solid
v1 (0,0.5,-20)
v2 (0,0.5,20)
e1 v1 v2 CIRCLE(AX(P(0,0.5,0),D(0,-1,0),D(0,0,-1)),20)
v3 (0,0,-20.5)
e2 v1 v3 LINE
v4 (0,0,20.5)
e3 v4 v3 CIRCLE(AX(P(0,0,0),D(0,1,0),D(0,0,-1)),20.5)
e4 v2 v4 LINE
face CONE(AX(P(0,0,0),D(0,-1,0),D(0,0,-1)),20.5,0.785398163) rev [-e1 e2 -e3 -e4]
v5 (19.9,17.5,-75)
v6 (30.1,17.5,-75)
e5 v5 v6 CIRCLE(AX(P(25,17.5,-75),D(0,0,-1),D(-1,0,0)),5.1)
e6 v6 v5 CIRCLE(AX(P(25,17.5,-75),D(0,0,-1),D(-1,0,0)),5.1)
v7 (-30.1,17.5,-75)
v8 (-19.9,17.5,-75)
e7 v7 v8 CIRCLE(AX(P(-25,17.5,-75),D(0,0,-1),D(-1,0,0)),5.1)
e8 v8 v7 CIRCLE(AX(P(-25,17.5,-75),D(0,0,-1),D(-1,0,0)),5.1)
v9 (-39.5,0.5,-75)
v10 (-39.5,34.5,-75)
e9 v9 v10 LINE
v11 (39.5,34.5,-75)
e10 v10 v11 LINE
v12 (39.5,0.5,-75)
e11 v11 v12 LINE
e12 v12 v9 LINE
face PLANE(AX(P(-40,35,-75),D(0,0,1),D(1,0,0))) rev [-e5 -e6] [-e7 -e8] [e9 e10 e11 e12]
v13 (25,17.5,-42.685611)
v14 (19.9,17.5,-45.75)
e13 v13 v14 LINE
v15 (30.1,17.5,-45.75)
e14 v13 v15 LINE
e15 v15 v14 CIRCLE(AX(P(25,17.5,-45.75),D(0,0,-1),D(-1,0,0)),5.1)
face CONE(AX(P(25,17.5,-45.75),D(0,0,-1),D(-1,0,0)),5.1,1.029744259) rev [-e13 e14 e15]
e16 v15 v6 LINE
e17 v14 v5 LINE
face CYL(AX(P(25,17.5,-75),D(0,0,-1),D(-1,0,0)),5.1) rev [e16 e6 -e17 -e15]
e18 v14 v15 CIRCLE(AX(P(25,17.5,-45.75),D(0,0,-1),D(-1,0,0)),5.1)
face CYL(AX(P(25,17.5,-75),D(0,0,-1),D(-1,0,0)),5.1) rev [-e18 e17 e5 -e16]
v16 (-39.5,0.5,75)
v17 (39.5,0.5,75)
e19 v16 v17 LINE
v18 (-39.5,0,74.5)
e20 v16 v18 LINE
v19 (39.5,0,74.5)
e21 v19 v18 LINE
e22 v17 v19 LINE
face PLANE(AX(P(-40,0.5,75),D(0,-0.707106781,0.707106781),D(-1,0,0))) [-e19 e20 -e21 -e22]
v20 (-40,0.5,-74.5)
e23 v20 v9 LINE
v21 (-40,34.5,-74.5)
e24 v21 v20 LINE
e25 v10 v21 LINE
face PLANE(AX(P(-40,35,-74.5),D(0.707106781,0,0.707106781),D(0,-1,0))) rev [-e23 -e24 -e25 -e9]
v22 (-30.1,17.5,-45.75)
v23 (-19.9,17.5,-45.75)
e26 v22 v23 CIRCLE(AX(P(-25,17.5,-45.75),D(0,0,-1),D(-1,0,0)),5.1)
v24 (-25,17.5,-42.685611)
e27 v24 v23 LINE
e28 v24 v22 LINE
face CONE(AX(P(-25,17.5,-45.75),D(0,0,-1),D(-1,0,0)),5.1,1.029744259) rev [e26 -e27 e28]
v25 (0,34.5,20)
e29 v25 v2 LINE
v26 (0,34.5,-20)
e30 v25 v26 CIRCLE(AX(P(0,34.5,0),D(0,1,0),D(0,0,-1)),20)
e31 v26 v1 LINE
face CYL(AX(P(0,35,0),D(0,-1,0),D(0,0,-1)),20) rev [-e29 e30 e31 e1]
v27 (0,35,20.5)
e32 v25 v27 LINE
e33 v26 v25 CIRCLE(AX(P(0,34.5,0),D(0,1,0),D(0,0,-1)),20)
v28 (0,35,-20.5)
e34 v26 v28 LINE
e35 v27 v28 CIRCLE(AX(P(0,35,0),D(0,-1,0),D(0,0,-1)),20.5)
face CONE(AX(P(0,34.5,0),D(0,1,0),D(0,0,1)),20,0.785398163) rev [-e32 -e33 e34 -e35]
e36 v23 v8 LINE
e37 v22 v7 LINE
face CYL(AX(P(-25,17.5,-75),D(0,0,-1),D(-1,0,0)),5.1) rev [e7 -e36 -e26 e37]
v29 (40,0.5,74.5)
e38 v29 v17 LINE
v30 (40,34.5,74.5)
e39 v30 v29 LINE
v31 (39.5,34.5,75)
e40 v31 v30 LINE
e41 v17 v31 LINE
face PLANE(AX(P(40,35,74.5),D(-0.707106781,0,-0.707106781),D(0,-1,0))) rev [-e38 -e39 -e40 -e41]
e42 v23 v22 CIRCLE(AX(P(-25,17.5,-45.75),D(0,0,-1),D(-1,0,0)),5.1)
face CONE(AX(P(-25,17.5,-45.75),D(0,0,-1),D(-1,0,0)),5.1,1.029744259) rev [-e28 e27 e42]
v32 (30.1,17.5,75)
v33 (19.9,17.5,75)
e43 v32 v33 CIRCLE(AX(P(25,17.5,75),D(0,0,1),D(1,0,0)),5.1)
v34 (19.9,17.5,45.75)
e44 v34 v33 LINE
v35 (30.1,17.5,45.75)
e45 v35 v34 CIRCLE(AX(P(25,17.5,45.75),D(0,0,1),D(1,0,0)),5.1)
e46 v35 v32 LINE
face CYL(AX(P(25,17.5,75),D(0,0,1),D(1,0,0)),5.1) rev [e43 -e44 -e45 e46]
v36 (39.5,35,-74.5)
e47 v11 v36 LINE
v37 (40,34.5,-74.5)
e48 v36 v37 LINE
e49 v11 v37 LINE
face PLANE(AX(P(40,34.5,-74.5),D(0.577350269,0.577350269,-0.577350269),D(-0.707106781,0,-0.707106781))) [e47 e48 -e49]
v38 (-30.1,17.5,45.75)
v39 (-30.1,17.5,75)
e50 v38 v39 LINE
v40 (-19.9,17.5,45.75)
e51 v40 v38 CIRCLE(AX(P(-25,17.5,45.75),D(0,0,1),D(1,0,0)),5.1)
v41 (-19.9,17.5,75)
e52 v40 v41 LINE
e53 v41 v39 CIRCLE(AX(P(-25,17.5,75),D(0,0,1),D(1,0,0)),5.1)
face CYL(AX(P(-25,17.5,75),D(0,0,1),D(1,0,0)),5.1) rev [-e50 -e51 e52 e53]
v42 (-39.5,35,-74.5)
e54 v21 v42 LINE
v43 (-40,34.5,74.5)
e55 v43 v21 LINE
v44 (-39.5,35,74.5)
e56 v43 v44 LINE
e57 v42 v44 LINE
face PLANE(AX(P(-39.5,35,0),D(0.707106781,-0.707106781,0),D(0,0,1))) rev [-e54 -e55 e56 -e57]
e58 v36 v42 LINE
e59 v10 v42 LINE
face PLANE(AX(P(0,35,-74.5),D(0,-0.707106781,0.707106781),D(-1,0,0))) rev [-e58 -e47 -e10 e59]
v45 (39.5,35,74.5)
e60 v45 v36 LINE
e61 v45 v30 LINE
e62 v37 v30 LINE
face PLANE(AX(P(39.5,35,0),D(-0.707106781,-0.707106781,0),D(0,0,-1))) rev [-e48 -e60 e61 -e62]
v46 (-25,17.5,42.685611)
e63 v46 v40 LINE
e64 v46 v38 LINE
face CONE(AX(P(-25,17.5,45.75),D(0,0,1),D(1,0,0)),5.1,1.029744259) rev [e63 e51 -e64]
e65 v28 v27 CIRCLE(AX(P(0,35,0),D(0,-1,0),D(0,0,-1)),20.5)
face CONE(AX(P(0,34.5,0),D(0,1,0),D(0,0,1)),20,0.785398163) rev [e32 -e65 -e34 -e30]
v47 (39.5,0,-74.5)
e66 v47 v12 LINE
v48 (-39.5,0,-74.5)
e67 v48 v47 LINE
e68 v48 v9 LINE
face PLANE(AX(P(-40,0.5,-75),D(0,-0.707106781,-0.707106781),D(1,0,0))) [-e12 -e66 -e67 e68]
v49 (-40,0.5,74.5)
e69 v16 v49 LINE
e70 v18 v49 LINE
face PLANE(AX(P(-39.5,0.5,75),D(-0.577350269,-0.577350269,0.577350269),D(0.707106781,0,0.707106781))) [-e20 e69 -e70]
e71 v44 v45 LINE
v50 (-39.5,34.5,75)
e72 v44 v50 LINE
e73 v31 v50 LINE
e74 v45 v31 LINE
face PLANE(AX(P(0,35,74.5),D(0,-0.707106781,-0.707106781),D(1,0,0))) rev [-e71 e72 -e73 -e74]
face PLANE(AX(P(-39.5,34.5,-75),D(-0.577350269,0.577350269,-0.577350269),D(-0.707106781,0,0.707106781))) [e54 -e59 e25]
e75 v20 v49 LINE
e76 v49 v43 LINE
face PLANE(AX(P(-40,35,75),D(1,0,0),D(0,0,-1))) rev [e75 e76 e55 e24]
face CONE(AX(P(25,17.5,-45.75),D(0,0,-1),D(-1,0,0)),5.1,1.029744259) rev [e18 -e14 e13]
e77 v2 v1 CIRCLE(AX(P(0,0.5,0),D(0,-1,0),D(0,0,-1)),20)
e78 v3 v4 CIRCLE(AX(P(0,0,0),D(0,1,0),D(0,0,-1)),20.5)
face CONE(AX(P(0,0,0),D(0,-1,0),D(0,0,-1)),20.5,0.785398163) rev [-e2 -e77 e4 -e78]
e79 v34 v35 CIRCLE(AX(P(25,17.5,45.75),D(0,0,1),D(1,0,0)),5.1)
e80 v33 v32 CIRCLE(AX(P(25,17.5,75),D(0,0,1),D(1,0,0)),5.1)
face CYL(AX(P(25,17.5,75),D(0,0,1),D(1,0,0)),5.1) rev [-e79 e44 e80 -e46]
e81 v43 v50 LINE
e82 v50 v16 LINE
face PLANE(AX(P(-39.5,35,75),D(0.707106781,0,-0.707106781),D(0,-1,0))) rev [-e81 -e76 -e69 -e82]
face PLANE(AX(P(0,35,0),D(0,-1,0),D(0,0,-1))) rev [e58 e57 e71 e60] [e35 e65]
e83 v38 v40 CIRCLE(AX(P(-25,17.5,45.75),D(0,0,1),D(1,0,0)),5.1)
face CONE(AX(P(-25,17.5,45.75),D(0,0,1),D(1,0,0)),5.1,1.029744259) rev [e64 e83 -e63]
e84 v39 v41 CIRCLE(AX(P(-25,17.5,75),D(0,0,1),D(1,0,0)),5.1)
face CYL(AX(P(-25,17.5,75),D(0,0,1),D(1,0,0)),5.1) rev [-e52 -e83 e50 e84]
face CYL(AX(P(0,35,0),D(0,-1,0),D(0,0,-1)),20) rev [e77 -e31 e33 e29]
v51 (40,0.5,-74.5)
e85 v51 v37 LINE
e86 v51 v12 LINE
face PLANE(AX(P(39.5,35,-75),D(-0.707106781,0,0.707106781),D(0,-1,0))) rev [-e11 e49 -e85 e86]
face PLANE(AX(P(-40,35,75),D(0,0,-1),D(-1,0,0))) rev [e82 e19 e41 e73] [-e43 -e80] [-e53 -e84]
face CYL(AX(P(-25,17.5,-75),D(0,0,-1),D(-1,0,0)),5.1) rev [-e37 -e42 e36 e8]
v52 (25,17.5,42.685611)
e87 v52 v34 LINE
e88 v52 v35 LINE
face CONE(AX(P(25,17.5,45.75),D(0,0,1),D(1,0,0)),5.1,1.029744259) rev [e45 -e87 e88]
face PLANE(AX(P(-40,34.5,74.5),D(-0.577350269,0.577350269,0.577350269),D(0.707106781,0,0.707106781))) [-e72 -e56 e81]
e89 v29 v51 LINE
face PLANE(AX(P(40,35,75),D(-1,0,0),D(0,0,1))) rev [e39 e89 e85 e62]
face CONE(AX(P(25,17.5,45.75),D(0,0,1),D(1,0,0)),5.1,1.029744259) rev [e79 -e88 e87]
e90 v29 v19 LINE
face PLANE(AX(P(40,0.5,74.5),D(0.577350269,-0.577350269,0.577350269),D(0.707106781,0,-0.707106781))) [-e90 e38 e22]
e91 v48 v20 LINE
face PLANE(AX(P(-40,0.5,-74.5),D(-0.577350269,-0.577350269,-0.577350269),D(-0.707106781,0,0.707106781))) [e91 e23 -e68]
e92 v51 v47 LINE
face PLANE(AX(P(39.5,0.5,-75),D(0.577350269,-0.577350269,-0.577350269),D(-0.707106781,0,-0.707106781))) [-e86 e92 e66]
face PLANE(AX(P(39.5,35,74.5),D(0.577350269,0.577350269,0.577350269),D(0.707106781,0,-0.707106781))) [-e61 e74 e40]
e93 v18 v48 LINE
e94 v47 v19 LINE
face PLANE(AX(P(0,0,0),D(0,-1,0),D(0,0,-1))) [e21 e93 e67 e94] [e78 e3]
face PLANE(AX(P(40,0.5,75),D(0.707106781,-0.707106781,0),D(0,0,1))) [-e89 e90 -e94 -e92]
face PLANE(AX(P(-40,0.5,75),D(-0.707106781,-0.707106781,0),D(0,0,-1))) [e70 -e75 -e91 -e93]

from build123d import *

# Parameters (mm, degrees)
SKETCH_1_W              = 80
SKETCH_1_H              = 150
SKETCH_1_R              = 20
EXTRUDE_1_DEPTH         = 35
CHAMFER_1_SIZE          = 0.5
HOLE_WIZARD_M12_1_D     = 10.2
HOLE_WIZARD_M12_1_DEPTH = 29.25
HOLE_WIZARD_M12_1_TIP   = 3.064389157
HOLE_WIZARD_M12_2_D     = 10.2
HOLE_WIZARD_M12_2_DEPTH = 29.25
HOLE_WIZARD_M12_2_TIP   = 3.064389157


with BuildPart() as part:
    # 草图1 → 凸台-拉伸1 (new body)
    with BuildSketch(Plane(origin=(0, 0, 0), x_dir=(1, 0, 0), z_dir=(0, 1, 0))):
        Rectangle(SKETCH_1_W, SKETCH_1_H)
        with Locations(Location((0, 0, 0), (0, 0, 270))):
            Circle(SKETCH_1_R, mode=Mode.SUBTRACT)
    extrude(amount=EXTRUDE_1_DEPTH)

    # 倒角1
    chamfer_1_edges = [part.edges().sort_by_distance(p)[0] for p in [
        (-40, 35, 0),
        (0, 0, -20),
        (0, 35, -20),
        (0, 35, 75),
        (40, 35, 0),
        (0, 0, 75),
        (-40, 0, 0),
        (0, 0, -75),
        (40, 0, 0),
        (0, 35, -75),
        (40, 17.5, 75),
        (-40, 17.5, 75),
        (-40, 17.5, -75),
        (40, 17.5, -75),
    ]]
    chamfer(chamfer_1_edges, length=CHAMFER_1_SIZE)

    # M12 螺纹孔1
    with Locations(Plane.XY.offset(75)):
        with Locations((25, 17.5), (-25, 17.5)):
            Hole(HOLE_WIZARD_M12_1_D / 2, depth=HOLE_WIZARD_M12_1_DEPTH)
            with Locations((0, 0, -(HOLE_WIZARD_M12_1_DEPTH + HOLE_WIZARD_M12_1_TIP / 2))):  # 118° drill point
                Cone(0, HOLE_WIZARD_M12_1_D / 2, HOLE_WIZARD_M12_1_TIP, mode=Mode.SUBTRACT)

    # M12 螺纹孔2
    with Locations(Plane(origin=(0, 0, -75), x_dir=(-1, 0, 0), z_dir=(0, 0, -1))):
        with Locations((-25, 17.5), (25, 17.5)):
            Hole(HOLE_WIZARD_M12_2_D / 2, depth=HOLE_WIZARD_M12_2_DEPTH)
            with Locations((0, 0, -(HOLE_WIZARD_M12_2_DEPTH + HOLE_WIZARD_M12_2_TIP / 2))):  # 118° drill point
                Cone(0, HOLE_WIZARD_M12_2_D / 2, HOLE_WIZARD_M12_2_TIP, mode=Mode.SUBTRACT)


solid = part.part
